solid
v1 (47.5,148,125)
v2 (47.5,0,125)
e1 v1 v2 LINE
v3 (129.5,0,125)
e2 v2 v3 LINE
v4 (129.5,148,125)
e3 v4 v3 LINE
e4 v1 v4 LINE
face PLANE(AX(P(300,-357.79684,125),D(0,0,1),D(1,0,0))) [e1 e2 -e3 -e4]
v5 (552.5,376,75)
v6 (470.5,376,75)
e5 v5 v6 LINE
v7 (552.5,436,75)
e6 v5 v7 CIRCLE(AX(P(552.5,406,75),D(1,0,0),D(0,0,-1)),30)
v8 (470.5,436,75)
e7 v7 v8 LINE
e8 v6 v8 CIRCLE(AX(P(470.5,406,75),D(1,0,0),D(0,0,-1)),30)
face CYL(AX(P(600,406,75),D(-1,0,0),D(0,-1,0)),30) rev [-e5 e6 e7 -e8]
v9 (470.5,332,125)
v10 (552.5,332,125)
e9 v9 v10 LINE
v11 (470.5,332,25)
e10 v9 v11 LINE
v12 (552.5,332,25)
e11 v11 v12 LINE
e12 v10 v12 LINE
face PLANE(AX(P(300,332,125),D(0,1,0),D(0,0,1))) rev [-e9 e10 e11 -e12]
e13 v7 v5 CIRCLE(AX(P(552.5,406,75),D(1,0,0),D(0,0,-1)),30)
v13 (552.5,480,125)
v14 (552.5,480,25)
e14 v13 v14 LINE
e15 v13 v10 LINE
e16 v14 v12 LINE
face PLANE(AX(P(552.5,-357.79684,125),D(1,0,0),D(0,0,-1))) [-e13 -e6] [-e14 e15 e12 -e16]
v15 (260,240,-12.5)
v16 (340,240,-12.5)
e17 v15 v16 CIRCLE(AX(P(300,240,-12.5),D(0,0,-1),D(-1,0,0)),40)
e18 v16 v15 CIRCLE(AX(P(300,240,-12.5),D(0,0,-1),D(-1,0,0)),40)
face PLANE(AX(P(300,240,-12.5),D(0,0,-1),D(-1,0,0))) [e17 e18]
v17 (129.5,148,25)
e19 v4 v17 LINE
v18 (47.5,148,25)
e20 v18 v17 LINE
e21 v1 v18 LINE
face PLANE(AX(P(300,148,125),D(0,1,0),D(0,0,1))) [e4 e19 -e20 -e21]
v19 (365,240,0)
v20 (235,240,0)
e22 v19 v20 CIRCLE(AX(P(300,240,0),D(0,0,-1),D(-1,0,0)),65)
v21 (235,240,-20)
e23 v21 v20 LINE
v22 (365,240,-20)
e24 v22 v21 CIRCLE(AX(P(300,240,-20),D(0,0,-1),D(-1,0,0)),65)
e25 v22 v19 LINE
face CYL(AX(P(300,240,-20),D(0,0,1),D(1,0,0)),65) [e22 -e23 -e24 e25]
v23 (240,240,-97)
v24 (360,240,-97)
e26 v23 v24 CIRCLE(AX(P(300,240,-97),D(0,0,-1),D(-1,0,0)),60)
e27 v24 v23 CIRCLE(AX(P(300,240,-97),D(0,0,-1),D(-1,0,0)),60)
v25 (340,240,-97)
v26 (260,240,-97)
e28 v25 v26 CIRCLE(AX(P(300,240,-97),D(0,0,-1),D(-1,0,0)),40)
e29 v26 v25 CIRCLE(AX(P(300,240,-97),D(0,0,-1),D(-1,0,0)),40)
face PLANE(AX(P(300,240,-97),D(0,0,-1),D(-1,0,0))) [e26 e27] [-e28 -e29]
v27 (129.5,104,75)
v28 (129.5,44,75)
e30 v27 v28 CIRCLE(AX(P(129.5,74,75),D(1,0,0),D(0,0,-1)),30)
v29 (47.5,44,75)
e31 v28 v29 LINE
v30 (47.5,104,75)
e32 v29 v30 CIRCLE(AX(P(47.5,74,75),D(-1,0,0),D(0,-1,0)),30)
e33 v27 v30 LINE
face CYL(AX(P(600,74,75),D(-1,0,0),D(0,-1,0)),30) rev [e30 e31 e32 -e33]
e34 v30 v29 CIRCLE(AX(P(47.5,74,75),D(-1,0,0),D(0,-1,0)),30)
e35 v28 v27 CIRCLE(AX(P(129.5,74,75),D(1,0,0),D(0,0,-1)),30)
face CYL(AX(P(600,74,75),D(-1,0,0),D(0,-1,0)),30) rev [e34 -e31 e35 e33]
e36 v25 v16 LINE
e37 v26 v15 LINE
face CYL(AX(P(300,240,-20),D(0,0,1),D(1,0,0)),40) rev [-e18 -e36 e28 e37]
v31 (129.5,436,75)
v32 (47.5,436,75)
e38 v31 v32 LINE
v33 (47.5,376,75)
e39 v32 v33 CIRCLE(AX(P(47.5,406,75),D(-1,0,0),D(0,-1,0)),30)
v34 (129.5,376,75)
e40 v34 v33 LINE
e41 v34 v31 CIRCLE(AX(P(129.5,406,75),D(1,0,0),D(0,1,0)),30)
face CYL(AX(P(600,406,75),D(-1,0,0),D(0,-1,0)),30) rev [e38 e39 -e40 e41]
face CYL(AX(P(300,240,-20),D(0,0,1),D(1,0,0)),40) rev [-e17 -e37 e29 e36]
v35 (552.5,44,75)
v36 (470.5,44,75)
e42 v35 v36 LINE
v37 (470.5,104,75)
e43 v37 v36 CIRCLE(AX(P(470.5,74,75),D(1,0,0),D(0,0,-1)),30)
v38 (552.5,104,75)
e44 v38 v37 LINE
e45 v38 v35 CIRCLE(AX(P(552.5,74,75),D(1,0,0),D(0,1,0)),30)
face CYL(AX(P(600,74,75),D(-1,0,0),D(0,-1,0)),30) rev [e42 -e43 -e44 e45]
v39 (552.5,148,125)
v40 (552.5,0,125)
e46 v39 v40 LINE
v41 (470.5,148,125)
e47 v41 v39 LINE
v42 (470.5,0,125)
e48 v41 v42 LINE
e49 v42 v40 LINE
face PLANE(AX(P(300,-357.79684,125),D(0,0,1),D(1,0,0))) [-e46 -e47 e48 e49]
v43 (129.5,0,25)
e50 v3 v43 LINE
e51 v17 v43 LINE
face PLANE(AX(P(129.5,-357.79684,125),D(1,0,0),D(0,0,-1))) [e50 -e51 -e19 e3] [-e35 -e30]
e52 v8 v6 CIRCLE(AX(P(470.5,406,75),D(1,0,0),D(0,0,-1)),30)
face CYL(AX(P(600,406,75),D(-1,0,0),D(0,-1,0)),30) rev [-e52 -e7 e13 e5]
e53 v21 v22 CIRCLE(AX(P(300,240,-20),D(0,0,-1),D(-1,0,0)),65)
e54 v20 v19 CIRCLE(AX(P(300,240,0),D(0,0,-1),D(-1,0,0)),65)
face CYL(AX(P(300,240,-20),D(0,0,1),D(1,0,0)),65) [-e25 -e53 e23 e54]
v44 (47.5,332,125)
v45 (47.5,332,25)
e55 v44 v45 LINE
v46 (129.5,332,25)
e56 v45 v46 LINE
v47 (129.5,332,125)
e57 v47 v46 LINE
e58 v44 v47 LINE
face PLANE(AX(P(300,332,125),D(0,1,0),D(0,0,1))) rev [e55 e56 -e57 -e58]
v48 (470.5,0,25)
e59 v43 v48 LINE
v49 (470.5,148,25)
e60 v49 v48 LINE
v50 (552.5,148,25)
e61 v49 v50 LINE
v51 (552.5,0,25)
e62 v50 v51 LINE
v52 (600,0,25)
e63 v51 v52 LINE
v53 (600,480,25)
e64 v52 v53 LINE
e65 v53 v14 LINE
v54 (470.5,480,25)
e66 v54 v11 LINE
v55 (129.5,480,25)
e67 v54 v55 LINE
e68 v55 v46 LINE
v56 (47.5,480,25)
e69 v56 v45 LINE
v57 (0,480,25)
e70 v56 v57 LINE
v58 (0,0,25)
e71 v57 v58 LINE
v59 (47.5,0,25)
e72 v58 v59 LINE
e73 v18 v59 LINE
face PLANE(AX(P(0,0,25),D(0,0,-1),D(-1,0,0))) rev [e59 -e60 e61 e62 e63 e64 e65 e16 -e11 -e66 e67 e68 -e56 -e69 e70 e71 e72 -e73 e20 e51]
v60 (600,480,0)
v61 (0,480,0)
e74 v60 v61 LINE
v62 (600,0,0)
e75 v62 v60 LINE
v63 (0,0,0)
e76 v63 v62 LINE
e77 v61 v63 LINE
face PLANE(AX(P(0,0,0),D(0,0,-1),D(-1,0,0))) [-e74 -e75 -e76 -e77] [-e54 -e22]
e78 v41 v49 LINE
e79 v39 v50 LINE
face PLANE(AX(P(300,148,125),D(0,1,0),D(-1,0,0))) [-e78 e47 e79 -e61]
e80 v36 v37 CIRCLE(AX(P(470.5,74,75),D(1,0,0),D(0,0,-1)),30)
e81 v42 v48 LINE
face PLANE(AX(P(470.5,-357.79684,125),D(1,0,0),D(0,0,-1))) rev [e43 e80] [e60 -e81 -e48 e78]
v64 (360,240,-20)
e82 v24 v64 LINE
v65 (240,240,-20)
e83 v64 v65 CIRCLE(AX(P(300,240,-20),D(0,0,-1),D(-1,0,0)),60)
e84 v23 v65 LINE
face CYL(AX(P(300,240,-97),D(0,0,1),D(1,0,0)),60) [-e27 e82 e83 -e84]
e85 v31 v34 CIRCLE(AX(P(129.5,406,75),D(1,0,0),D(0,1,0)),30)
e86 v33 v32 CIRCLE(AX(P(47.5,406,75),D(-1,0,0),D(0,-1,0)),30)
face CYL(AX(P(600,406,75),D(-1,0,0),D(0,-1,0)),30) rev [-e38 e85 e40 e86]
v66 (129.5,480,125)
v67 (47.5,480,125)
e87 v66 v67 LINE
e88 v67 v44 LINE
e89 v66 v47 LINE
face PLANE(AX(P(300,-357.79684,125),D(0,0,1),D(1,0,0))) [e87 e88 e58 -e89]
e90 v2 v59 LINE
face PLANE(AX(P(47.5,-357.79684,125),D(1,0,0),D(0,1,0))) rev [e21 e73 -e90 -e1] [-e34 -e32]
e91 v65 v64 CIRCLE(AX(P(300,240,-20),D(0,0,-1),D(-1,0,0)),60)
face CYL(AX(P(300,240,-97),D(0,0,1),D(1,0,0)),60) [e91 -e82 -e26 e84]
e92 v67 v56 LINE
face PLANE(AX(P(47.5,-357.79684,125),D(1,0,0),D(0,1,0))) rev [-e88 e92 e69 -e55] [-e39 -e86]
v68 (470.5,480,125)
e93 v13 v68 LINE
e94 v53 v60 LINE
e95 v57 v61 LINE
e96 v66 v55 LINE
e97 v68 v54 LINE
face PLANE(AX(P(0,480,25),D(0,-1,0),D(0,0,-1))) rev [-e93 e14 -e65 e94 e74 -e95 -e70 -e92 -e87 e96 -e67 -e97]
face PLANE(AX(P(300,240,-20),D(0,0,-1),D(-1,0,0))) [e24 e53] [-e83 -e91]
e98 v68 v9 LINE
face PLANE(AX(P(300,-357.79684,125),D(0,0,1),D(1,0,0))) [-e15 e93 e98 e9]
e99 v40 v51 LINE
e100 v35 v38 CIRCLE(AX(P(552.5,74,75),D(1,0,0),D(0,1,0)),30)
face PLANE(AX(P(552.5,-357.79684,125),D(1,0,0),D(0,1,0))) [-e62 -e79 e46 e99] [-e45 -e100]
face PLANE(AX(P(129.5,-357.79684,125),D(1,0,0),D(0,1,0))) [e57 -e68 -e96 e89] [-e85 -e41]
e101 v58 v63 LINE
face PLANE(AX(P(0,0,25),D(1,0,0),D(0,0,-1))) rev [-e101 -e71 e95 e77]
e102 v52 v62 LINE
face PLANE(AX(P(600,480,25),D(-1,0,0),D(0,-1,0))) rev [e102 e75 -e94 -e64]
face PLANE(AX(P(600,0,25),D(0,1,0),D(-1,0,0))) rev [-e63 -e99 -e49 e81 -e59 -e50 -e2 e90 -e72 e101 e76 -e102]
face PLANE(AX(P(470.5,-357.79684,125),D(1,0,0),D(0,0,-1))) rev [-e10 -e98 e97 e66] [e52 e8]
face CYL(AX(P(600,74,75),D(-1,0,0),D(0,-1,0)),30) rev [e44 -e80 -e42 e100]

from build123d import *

# Parameters (mm, degrees)
SKETCH1_W           = 600
SKETCH1_H           = 480
BOSS_EXTRUDE1_DEPTH = 25
SKETCH2_W           = 82
SKETCH2_H           = 148
BOSS_EXTRUDE2_DEPTH = 100
SKETCH4_R           = 30
CUT_EXTRUDE1_DEPTH  = 743.483164792
SKETCH5_R           = 65
SKETCH5_R_2         = 40
BOSS_EXTRUDE3_DEPTH = 20
SKETCH6_R           = 60
SKETCH6_R_2         = 40
BOSS_EXTRUDE4_DEPTH = 77
SKETCH7_R           = 40
BOSS_EXTRUDE5_DEPTH = 12.5


with BuildPart() as part:
    # Sketch1 → Boss-Extrude1 (new body)
    with BuildSketch(Plane.XY):
        with Locations((300, 240)):
            Rectangle(SKETCH1_W, SKETCH1_H)
    extrude(amount=BOSS_EXTRUDE1_DEPTH)

    # Sketch2 → Boss-Extrude2 (add)
    with BuildSketch(Plane.XY.offset(25)):
        with Locations((88.5, 406)):
            Rectangle(SKETCH2_W, SKETCH2_H)
        with Locations((88.5, 74)):
            Rectangle(SKETCH2_W, SKETCH2_H)
        with Locations((511.5, 74)):
            Rectangle(SKETCH2_W, SKETCH2_H)
        with Locations((511.5, 406)):
            Rectangle(SKETCH2_W, SKETCH2_H)
    extrude(amount=BOSS_EXTRUDE2_DEPTH)

    # Sketch4 → Cut-Extrude1 (cut, through all)
    with BuildSketch(Plane.ZY.offset(-47.5)):
        with Locations(Location((75, 406, 0), (0, 0, 180))):
            Circle(SKETCH4_R)
        with Locations(Location((75, 74, 0), (0, 0, 180))):
            Circle(SKETCH4_R)
    extrude(amount=-CUT_EXTRUDE1_DEPTH, mode=Mode.SUBTRACT)

    # Sketch5 → Boss-Extrude3 (add)
    with BuildSketch(Plane(origin=(0, 0, 0), x_dir=(-1, 0, 0), z_dir=(0, 0, -1))):
        with Locations((-300, 240)):
            Circle(SKETCH5_R)
        with Locations((-300, 240)):
            Circle(SKETCH5_R_2, mode=Mode.SUBTRACT)
    extrude(amount=BOSS_EXTRUDE3_DEPTH)

    # Sketch6 → Boss-Extrude4 (add)
    with BuildSketch(Plane(origin=(0, 0, -20), x_dir=(-1, 0, 0), z_dir=(0, 0, -1))):
        with Locations((-300, 240)):
            Circle(SKETCH6_R)
        with Locations((-300, 240)):
            Circle(SKETCH6_R_2, mode=Mode.SUBTRACT)
    extrude(amount=BOSS_EXTRUDE4_DEPTH)

    # Sketch7 → Boss-Extrude5 (add)
    with BuildSketch(Plane(origin=(0, 0, 0), x_dir=(-1, 0, 0), z_dir=(0, 0, -1))):
        with Locations((-300, 240)):
            Circle(SKETCH7_R)
    extrude(amount=BOSS_EXTRUDE5_DEPTH)


solid = part.part
